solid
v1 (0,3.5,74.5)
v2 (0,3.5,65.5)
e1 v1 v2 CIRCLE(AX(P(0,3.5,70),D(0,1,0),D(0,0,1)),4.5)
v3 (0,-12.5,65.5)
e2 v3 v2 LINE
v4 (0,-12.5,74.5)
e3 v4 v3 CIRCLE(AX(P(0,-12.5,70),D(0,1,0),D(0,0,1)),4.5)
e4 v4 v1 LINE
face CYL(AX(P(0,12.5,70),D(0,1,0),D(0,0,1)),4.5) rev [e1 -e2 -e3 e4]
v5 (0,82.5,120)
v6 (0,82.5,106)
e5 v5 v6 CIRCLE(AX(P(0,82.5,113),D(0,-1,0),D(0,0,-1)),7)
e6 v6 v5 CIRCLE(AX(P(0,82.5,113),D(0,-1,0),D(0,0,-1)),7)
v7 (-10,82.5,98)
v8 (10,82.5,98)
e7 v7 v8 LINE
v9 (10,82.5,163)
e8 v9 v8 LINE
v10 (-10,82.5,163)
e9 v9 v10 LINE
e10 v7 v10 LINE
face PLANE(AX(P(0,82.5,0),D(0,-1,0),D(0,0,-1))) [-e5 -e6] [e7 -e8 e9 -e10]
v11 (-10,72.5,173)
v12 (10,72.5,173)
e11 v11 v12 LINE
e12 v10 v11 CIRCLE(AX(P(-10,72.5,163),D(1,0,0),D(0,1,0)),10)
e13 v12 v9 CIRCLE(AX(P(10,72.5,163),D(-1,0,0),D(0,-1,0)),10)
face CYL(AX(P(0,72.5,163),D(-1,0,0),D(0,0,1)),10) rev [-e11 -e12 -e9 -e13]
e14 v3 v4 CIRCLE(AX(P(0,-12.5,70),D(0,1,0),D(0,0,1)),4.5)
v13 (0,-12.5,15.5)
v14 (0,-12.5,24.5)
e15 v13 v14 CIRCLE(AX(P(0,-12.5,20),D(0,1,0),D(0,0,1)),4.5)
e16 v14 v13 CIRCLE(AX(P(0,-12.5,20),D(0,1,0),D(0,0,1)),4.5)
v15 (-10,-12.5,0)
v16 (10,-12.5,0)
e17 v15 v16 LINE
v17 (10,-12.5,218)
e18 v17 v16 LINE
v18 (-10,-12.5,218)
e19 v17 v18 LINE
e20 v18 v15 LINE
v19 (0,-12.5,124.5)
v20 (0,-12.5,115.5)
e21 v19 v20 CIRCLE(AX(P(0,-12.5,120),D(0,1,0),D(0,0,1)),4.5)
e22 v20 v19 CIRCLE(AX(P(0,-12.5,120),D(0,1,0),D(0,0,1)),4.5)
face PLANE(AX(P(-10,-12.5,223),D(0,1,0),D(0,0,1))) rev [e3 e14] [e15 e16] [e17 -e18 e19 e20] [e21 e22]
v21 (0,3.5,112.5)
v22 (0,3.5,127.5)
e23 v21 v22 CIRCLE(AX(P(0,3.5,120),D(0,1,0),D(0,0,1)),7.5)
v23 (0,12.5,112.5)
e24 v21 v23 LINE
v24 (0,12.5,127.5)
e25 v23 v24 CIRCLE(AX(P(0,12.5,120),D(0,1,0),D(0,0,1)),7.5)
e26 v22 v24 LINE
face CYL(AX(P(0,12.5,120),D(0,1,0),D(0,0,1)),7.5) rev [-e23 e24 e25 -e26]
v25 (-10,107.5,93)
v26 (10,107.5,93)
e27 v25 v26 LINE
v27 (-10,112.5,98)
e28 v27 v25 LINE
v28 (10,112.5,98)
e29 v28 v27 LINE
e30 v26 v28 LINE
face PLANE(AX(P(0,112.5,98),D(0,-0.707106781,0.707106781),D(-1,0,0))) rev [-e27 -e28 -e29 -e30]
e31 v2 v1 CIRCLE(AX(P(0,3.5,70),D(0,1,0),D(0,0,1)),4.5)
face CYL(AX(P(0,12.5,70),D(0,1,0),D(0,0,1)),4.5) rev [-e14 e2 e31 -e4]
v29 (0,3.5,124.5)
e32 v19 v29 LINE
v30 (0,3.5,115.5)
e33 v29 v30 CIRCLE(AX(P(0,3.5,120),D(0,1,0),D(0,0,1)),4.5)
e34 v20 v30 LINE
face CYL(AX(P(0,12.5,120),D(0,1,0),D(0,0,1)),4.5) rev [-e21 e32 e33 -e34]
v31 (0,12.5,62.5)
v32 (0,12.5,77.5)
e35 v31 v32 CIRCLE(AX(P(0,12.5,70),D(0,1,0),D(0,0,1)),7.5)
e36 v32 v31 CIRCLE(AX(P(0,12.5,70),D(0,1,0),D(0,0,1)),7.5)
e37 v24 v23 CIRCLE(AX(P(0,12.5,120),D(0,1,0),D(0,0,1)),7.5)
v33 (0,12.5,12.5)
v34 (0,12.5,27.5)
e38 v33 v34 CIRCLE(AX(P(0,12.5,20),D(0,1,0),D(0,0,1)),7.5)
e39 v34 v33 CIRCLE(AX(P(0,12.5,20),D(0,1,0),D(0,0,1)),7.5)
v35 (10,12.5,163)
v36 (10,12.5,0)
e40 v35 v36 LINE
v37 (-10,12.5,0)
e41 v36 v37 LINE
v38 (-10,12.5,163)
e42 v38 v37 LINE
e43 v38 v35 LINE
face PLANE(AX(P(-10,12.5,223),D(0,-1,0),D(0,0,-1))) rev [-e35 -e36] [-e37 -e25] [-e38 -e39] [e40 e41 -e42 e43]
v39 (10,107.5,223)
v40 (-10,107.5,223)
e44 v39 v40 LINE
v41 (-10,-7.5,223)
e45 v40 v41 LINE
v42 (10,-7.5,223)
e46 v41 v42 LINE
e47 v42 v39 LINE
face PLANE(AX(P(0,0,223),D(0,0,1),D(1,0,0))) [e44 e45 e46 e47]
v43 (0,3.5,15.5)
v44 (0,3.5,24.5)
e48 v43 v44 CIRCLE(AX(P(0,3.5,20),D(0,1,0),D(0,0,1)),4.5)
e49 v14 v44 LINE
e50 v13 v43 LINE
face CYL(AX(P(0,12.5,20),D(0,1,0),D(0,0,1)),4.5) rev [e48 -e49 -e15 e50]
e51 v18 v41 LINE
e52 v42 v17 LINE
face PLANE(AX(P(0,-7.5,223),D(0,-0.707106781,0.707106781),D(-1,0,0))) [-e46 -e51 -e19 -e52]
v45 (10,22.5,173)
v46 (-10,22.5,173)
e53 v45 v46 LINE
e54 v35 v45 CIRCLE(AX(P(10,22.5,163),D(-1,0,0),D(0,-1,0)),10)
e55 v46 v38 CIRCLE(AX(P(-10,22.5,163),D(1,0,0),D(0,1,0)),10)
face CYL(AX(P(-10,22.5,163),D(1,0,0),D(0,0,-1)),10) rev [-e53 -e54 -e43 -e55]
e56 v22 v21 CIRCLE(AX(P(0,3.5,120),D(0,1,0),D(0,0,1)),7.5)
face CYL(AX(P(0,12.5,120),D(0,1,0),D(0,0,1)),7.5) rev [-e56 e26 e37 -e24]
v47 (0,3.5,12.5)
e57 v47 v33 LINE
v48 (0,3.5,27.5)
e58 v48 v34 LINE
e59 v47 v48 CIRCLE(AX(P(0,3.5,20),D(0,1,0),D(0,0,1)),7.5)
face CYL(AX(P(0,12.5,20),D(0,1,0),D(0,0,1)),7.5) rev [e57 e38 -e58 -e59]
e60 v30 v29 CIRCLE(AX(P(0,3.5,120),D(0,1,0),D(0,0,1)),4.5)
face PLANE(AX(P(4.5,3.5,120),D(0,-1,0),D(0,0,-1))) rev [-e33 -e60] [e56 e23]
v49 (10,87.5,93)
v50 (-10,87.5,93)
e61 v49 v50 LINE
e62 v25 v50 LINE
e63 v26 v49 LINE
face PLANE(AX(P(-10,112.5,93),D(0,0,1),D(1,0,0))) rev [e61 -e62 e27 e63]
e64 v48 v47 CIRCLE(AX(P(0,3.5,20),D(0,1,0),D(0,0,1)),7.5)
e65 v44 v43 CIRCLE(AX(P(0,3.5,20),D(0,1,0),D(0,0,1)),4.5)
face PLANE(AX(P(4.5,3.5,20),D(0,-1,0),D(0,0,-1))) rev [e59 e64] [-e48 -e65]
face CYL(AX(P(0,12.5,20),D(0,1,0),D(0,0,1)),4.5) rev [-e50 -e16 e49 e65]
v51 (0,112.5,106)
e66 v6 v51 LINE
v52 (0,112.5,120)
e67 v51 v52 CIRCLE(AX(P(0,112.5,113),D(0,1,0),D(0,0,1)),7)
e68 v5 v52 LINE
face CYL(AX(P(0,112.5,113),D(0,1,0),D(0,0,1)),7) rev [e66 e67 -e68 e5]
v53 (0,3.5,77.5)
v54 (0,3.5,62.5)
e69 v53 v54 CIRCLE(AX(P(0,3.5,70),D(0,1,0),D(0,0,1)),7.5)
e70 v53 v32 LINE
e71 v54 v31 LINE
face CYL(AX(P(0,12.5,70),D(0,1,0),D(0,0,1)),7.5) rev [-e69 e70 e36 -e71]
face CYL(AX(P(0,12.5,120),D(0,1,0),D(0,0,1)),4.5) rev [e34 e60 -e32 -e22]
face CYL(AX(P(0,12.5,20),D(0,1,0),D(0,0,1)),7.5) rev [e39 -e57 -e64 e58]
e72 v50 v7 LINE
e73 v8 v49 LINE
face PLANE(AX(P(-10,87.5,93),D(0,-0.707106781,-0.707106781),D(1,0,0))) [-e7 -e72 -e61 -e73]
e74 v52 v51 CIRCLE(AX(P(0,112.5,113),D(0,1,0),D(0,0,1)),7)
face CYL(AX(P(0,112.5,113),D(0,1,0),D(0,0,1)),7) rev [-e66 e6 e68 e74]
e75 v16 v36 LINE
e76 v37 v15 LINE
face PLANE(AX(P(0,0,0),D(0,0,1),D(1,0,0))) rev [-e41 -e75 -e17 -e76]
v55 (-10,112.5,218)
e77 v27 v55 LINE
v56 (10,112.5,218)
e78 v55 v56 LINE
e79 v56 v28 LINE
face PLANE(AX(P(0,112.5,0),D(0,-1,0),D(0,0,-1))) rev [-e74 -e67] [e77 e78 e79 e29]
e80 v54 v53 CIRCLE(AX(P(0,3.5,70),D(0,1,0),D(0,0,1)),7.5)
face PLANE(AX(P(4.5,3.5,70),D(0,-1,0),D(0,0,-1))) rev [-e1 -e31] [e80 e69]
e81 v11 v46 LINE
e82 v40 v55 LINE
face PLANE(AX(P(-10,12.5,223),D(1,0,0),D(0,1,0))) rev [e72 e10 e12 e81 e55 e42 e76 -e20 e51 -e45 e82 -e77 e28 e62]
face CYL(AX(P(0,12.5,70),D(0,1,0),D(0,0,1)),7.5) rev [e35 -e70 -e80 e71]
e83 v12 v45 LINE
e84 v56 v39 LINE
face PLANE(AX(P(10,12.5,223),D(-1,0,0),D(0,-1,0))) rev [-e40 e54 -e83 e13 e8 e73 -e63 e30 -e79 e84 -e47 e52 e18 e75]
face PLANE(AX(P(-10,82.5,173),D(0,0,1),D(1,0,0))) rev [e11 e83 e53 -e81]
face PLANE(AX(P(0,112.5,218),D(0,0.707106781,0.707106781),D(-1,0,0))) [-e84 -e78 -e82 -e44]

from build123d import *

# Parameters (mm, degrees)
SKETCH_1_W                = 20
SKETCH_1_H                = 25
EXTRUDE_1_DEPTH           = 223
HOLE_WIZARD_1_D           = 9
HOLE_WIZARD_1_CBORE_D     = 15
HOLE_WIZARD_1_CBORE_DEPTH = 9
PATTERN_LINEAR_1_COUNT    = 3
PATTERN_LINEAR_1_PITCH    = 50
SKETCH_6_W                = 20
SKETCH_6_H                = 50
EXTRUDE_3_DEPTH           = 70
SKETCH_7_W                = 20
SKETCH_7_H                = 130
EXTRUDE_4_DEPTH           = 30
HOLE_WIZARD_M16_1_D       = 14
HOLE_WIZARD_M16_1_DEPTH   = 38
HOLE_WIZARD_M16_1_TIP     = 4.206024333
CHAMFER_1_SIZE            = 5
FILLET_1_R                = 10
CHAMFER_2_SIZE            = 5


with BuildPart() as part:
    # 草图1 → 凸台-拉伸1 (new body)
    with BuildSketch(Plane.XY):
        Rectangle(SKETCH_1_W, SKETCH_1_H)
    extrude(amount=EXTRUDE_1_DEPTH)

    # 打孔尺寸(%根据)内六角圆柱头螺钉的类型1 (through all)
    with Locations(Plane(origin=(0, 12.5, 0), x_dir=(1, 0, 0), z_dir=(0, 1, 0))):
        with Locations((0, -20)):
            hole_wizard_1 = CounterBoreHole(HOLE_WIZARD_1_D / 2, HOLE_WIZARD_1_CBORE_D / 2, HOLE_WIZARD_1_CBORE_DEPTH)

    # 阵列(线性)1: 打孔尺寸(%根据)内六角圆柱头螺钉的类型1 ×3
    with Locations(*[(0, 0, i * PATTERN_LINEAR_1_PITCH) for i in range(1, PATTERN_LINEAR_1_COUNT)]):
        add(hole_wizard_1, mode=Mode.SUBTRACT)

    # 草图6 → 凸台-拉伸3 (add)
    with BuildSketch(Plane(origin=(0, 12.5, 0), x_dir=(1, 0, 0), z_dir=(0, 1, 0))):
        with Locations((0, -198)):
            Rectangle(SKETCH_6_W, SKETCH_6_H)
    extrude(amount=EXTRUDE_3_DEPTH)

    # 草图7 → 凸台-拉伸4 (add)
    with BuildSketch(Plane(origin=(0, 82.5, 0), x_dir=(1, 0, 0), z_dir=(0, 1, 0))):
        with Locations((0, -158)):
            Rectangle(SKETCH_7_W, SKETCH_7_H)
    extrude(amount=EXTRUDE_4_DEPTH)

    # M16 螺纹孔1
    with Locations(Plane(origin=(0, 112.5, 0), x_dir=(1, 0, 0), z_dir=(0, 1, 0))):
        with Locations((0, -113)):
            Hole(HOLE_WIZARD_M16_1_D / 2, depth=HOLE_WIZARD_M16_1_DEPTH)
            with Locations((0, 0, -(HOLE_WIZARD_M16_1_DEPTH + HOLE_WIZARD_M16_1_TIP / 2))):  # 118° drill point
                Cone(0, HOLE_WIZARD_M16_1_D / 2, HOLE_WIZARD_M16_1_TIP, mode=Mode.SUBTRACT)

    # 倒角1
    chamfer_1_edges = [part.edges().sort_by_distance(p)[0] for p in [
        (0, 82.5, 93),
        (0, 112.5, 93),
    ]]
    chamfer(chamfer_1_edges, length=CHAMFER_1_SIZE)

    # 圆角1
    fillet_1_edges = [part.edges().sort_by_distance(p)[0] for p in [
        (0, 12.5, 173),
        (0, 82.5, 173),
    ]]
    fillet(fillet_1_edges, radius=FILLET_1_R)

    # 倒角2
    chamfer_2_edges = [part.edges().sort_by_distance(p)[0] for p in [
        (0, -12.5, 223),
        (0, 112.5, 223),
    ]]
    chamfer(chamfer_2_edges, length=CHAMFER_2_SIZE)


solid = part.part
